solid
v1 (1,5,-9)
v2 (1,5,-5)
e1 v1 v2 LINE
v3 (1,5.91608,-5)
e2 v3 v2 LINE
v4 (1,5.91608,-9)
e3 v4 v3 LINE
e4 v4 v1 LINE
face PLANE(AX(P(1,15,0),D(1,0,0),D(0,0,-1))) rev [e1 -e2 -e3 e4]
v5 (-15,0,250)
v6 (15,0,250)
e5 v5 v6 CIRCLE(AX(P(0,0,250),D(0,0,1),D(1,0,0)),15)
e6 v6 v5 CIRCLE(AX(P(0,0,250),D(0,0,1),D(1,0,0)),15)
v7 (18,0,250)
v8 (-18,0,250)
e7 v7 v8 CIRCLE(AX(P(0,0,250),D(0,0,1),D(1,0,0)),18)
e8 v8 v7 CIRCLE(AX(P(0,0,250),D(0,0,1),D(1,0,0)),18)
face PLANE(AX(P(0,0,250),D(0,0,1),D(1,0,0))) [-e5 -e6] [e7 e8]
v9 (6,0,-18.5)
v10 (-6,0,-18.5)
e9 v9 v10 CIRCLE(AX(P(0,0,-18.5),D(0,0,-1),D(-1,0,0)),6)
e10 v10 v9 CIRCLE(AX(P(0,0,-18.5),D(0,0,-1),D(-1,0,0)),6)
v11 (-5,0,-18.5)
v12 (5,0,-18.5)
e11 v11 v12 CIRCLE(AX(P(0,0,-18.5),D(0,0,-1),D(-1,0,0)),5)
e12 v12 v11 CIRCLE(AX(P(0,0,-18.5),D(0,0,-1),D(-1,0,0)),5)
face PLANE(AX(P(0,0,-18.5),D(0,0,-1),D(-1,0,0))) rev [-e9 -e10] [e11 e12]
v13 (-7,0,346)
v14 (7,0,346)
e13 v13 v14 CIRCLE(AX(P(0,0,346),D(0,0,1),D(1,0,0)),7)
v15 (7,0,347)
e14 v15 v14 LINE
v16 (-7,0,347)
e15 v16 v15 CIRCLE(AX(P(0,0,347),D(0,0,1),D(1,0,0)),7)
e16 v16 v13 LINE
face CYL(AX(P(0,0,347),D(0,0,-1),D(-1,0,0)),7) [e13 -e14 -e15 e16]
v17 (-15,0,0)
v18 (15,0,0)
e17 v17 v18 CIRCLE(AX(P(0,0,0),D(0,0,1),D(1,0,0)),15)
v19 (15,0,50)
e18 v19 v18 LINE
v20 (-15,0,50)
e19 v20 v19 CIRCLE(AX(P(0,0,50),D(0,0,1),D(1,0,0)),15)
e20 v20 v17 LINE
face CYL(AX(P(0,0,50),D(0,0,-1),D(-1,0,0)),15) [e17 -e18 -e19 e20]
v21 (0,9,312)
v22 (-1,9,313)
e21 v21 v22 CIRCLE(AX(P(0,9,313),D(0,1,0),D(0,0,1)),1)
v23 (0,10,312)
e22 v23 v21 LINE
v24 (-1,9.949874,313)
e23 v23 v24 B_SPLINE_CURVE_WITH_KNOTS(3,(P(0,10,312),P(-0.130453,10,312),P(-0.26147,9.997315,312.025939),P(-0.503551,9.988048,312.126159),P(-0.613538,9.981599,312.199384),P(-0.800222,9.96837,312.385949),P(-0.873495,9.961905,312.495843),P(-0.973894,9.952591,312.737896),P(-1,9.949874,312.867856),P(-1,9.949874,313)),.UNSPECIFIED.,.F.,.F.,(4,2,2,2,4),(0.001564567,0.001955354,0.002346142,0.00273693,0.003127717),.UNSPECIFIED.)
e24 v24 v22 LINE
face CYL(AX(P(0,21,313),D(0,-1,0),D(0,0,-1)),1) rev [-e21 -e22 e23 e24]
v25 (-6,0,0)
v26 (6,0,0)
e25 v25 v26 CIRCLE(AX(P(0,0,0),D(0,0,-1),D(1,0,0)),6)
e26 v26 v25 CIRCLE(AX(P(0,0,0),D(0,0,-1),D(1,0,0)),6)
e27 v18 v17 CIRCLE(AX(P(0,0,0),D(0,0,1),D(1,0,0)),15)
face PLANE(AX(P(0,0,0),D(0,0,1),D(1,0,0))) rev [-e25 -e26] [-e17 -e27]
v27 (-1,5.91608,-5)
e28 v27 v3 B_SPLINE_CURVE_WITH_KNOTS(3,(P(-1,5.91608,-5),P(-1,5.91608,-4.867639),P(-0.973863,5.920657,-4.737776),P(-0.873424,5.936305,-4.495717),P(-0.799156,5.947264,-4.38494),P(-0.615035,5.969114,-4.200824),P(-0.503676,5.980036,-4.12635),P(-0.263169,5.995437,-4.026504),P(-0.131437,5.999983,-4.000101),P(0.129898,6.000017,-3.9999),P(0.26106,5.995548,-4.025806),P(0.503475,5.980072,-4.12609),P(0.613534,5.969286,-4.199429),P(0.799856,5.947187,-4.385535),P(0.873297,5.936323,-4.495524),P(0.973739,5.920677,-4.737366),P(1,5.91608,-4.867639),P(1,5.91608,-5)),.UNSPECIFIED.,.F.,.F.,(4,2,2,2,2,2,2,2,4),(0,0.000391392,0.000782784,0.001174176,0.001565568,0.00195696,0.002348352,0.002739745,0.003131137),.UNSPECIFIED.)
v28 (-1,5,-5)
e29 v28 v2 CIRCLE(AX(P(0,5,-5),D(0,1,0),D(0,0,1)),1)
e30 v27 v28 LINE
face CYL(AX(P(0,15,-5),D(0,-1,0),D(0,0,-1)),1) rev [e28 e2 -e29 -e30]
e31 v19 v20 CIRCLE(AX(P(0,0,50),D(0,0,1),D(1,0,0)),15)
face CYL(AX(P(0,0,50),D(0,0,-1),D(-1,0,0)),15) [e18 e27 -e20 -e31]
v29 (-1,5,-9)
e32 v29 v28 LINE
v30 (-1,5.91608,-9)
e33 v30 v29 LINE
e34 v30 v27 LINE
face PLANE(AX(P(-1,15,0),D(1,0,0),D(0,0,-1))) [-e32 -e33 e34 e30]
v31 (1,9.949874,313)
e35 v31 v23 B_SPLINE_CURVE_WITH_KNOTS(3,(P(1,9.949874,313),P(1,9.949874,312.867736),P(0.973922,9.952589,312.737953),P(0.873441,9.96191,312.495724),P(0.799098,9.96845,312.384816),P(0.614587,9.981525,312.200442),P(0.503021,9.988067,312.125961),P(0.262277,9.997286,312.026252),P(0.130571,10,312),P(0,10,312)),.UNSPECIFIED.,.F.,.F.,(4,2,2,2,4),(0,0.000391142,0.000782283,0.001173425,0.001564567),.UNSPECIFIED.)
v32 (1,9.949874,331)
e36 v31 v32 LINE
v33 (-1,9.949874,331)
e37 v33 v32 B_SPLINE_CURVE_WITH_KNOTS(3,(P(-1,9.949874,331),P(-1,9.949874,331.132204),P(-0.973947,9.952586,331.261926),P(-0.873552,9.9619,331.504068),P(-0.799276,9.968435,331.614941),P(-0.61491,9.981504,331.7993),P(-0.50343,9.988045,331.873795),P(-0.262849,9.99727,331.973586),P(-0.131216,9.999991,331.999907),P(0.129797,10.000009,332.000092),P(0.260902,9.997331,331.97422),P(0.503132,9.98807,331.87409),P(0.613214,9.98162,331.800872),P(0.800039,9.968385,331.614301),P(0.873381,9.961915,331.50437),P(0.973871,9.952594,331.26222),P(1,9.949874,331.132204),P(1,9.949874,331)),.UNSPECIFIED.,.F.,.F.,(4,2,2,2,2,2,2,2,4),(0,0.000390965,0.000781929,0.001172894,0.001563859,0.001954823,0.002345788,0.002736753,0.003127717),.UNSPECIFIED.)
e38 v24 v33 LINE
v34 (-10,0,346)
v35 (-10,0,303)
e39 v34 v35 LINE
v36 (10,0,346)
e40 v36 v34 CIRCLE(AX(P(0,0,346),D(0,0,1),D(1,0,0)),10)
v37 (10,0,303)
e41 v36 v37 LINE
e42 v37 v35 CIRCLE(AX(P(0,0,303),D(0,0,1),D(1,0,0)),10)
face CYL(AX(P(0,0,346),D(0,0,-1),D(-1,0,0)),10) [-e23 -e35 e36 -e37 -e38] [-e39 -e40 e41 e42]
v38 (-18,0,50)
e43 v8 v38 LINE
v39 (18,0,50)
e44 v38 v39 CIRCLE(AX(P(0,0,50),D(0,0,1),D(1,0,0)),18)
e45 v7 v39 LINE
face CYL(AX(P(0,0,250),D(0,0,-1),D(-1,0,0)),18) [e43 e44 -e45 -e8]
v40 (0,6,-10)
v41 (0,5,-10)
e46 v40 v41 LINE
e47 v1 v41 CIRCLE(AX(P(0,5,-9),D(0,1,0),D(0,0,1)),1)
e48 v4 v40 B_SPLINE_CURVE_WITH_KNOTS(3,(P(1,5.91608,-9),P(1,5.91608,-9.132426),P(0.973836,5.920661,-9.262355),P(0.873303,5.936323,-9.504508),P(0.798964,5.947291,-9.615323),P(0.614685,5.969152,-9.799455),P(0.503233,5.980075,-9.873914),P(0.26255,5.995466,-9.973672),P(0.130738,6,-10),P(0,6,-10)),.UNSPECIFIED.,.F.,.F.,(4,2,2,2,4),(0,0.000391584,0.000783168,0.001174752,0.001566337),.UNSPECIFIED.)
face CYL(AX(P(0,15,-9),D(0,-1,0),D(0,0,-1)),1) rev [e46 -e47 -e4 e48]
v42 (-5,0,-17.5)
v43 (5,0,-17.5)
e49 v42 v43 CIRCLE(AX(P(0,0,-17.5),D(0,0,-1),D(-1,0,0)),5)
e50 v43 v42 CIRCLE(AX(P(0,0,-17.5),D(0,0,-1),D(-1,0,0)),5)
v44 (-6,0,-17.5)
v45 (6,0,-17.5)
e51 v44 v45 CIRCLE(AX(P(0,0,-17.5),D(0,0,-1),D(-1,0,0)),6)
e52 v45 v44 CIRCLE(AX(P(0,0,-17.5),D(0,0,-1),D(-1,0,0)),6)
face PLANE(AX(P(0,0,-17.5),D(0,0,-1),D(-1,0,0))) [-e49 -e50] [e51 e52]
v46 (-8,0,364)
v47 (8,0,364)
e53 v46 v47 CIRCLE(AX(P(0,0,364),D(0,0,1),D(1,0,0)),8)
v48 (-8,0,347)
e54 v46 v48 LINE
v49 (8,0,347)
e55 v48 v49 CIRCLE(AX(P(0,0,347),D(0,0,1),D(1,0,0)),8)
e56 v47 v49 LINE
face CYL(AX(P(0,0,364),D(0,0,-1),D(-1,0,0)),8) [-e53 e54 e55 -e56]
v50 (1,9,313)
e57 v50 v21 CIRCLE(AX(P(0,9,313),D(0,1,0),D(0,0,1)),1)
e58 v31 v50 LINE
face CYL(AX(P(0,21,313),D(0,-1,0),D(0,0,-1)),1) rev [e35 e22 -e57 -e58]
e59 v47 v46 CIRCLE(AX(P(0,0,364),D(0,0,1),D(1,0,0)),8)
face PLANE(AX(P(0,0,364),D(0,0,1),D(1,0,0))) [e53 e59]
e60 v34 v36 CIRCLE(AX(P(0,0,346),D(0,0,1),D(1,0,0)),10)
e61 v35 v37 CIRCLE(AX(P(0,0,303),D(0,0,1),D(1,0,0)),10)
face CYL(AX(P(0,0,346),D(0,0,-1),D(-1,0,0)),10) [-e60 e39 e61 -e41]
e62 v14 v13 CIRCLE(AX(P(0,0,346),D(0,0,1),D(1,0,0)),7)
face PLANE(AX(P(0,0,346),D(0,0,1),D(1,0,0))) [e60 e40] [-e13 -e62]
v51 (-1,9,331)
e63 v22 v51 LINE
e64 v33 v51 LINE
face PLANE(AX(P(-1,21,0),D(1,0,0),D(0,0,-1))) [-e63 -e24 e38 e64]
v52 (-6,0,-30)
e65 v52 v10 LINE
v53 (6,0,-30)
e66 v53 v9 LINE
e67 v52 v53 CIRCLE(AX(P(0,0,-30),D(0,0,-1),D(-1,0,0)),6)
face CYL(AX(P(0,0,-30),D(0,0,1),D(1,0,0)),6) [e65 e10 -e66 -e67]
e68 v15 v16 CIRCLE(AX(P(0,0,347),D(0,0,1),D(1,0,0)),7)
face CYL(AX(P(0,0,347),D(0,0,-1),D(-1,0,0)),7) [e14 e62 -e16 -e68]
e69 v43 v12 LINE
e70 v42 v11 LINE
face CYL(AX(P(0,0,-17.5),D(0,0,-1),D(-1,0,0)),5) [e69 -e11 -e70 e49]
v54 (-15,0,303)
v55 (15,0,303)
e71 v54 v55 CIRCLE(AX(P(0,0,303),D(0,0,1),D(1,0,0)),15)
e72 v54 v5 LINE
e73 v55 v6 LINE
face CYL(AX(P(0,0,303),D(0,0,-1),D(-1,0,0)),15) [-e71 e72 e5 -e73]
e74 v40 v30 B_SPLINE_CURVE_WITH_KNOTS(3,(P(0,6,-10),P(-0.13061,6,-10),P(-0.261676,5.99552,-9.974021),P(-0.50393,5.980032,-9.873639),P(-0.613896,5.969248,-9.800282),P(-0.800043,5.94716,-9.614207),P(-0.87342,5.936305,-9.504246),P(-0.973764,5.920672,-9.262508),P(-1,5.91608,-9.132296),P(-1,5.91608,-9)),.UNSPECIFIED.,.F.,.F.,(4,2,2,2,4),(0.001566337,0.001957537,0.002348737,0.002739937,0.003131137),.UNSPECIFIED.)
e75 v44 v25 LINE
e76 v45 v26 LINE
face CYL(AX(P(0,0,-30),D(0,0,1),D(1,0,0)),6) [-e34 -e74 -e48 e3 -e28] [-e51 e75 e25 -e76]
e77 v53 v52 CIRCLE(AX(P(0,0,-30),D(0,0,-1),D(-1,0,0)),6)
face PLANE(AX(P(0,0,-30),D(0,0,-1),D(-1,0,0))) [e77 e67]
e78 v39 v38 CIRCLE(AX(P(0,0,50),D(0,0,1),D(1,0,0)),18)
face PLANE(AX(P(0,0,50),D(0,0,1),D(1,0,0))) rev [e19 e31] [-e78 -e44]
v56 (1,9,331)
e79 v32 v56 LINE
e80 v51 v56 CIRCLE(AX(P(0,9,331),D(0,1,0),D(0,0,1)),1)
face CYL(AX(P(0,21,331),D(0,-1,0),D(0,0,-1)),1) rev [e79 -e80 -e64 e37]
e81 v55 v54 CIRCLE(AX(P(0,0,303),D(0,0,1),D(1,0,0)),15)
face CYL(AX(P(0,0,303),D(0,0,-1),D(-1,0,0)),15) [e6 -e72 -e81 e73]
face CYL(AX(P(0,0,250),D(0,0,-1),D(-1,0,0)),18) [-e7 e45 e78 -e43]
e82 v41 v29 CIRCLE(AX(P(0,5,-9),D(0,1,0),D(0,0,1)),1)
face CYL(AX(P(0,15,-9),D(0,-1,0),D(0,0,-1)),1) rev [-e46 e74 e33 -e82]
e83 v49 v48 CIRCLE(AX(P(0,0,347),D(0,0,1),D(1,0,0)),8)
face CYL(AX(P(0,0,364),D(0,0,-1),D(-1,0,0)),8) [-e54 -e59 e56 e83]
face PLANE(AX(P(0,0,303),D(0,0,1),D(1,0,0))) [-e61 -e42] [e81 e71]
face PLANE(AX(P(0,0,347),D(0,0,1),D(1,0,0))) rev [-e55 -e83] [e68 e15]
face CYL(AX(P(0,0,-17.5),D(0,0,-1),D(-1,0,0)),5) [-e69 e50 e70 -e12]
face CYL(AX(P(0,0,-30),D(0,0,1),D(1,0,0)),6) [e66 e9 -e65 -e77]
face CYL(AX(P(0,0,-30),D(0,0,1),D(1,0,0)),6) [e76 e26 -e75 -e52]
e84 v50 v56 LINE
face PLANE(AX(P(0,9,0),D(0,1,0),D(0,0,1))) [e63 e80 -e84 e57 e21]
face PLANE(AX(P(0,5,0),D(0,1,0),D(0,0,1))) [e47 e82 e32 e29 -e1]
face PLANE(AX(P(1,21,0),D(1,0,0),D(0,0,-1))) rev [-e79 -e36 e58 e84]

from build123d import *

# Parameters (mm, degrees)
SKETCH1_R           = 15
BOSS_EXTRUDE1_DEPTH = 50
SKETCH2_R           = 18
BOSS_EXTRUDE2_DEPTH = 200
SKETCH3_R           = 15
BOSS_EXTRUDE3_DEPTH = 53
SKETCH4_R           = 6
BOSS_EXTRUDE4_DEPTH = 30
CUT_EXTRUDE1_START  = 5
CUT_EXTRUDE1_DEPTH  = 10
CUT_EXTRUDE3_START  = -12.5
SKETCH6_R           = 6
SKETCH6_R_2         = 5
CUT_EXTRUDE3_DEPTH  = 1
SKETCH7_R           = 10
BOSS_EXTRUDE5_DEPTH = 43
CUT_EXTRUDE4_START  = 4
CUT_EXTRUDE4_DEPTH  = 12
SKETCH8_R           = 8
BOSS_EXTRUDE6_DEPTH = 18
CUT_EXTRUDE6_START  = -18
SKETCH10_R          = 9
SKETCH10_R_2        = 7
CUT_EXTRUDE6_DEPTH  = 1


with BuildPart() as part:
    # Sketch1 → Boss-Extrude1 (new body)
    with BuildSketch(Plane.XY):
        Circle(SKETCH1_R)
    extrude(amount=BOSS_EXTRUDE1_DEPTH)

    # Sketch2 → Boss-Extrude2 (add)
    with BuildSketch(Plane.XY.offset(50)):
        Circle(SKETCH2_R)
    extrude(amount=BOSS_EXTRUDE2_DEPTH)

    # Sketch3 → Boss-Extrude3 (add)
    with BuildSketch(Plane.XY.offset(250)):
        Circle(SKETCH3_R)
    extrude(amount=BOSS_EXTRUDE3_DEPTH)

    # Sketch4 → Boss-Extrude4 (add)
    with BuildSketch(Plane(origin=(0, 0, 0), x_dir=(-1, 0, 0), z_dir=(0, 0, -1))):
        with Locations(Location((0, 0, 0), (0, 0, 180))):
            Circle(SKETCH4_R)
    extrude(amount=BOSS_EXTRUDE4_DEPTH)

    # Sketch5 → Cut-Extrude1 (cut)
    with BuildSketch(Plane(origin=(0, 0, 0), x_dir=(1, 0, 0), z_dir=(0, 1, 0)).offset(CUT_EXTRUDE1_START)):
        with BuildLine():
            ThreePointArc((-1, 9), (0, 8), (1, 9))
            Line((1, 9), (-1, 9))
        make_face()
        with BuildLine():
            Line((-1, 9), (1, 9))
            ThreePointArc((1, 9), (0, 10), (-1, 9))
        make_face()
        with BuildLine():
            Line((1, 5), (1, 9))
            ThreePointArc((1, 9), (0, 8), (-1, 9))
            Line((-1, 9), (-1, 5))
            ThreePointArc((-1, 5), (0, 6), (1, 5))
        make_face()
        with BuildLine():
            ThreePointArc((-1, 5), (0, 4), (1, 5))
            Line((1, 5), (-1, 5))
        make_face()
        with BuildLine():
            Line((-1, 5), (1, 5))
            ThreePointArc((1, 5), (0, 6), (-1, 5))
        make_face()
    extrude(amount=CUT_EXTRUDE1_DEPTH, mode=Mode.SUBTRACT)

    # Sketch6 → Cut-Extrude3 (cut)
    with BuildSketch(Plane(origin=(0, 0, -30), x_dir=(-1, 0, 0), z_dir=(0, 0, -1)).offset(CUT_EXTRUDE3_START)):
        with Locations(Location((0, 0, 0), (0, 0, 180))):
            Circle(SKETCH6_R)
        Circle(SKETCH6_R_2, mode=Mode.SUBTRACT)
    extrude(amount=CUT_EXTRUDE3_DEPTH, mode=Mode.SUBTRACT)

    # Sketch7 → Boss-Extrude5 (add)
    with BuildSketch(Plane.XY.offset(303)):
        Circle(SKETCH7_R)
    extrude(amount=BOSS_EXTRUDE5_DEPTH)

    # Sketch9 → Cut-Extrude4 (cut)
    with BuildSketch(Plane(origin=(0, 5, 0), x_dir=(1, 0, 0), z_dir=(0, 1, 0)).offset(CUT_EXTRUDE4_START)):
        with BuildLine():
            ThreePointArc((1, -313), (0, -314), (-1, -313))
            Line((-1, -313), (-1, -331))
            ThreePointArc((-1, -331), (0, -330), (1, -331))
            Line((1, -331), (1, -313))
        make_face()
        with BuildLine():
            ThreePointArc((1, -331), (0, -330), (-1, -331))
            Line((-1, -331), (1, -331))
        make_face()
        with BuildLine():
            Line((1, -331), (-1, -331))
            ThreePointArc((-1, -331), (0, -332), (1, -331))
        make_face()
        with BuildLine():
            ThreePointArc((1, -313), (0, -312), (-1, -313))
            Line((-1, -313), (1, -313))
        make_face()
        with BuildLine():
            Line((1, -313), (-1, -313))
            ThreePointArc((-1, -313), (0, -314), (1, -313))
        make_face()
    extrude(amount=CUT_EXTRUDE4_DEPTH, mode=Mode.SUBTRACT)

    # Sketch8 → Boss-Extrude6 (add)
    with BuildSketch(Plane.XY.offset(346)):
        Circle(SKETCH8_R)
    extrude(amount=BOSS_EXTRUDE6_DEPTH)

    # Sketch10 → Cut-Extrude6 (cut)
    with BuildSketch(Plane.XY.offset(364).offset(CUT_EXTRUDE6_START)):
        Circle(SKETCH10_R)
        Circle(SKETCH10_R_2, mode=Mode.SUBTRACT)
    extrude(amount=CUT_EXTRUDE6_DEPTH, mode=Mode.SUBTRACT)


solid = part.part
